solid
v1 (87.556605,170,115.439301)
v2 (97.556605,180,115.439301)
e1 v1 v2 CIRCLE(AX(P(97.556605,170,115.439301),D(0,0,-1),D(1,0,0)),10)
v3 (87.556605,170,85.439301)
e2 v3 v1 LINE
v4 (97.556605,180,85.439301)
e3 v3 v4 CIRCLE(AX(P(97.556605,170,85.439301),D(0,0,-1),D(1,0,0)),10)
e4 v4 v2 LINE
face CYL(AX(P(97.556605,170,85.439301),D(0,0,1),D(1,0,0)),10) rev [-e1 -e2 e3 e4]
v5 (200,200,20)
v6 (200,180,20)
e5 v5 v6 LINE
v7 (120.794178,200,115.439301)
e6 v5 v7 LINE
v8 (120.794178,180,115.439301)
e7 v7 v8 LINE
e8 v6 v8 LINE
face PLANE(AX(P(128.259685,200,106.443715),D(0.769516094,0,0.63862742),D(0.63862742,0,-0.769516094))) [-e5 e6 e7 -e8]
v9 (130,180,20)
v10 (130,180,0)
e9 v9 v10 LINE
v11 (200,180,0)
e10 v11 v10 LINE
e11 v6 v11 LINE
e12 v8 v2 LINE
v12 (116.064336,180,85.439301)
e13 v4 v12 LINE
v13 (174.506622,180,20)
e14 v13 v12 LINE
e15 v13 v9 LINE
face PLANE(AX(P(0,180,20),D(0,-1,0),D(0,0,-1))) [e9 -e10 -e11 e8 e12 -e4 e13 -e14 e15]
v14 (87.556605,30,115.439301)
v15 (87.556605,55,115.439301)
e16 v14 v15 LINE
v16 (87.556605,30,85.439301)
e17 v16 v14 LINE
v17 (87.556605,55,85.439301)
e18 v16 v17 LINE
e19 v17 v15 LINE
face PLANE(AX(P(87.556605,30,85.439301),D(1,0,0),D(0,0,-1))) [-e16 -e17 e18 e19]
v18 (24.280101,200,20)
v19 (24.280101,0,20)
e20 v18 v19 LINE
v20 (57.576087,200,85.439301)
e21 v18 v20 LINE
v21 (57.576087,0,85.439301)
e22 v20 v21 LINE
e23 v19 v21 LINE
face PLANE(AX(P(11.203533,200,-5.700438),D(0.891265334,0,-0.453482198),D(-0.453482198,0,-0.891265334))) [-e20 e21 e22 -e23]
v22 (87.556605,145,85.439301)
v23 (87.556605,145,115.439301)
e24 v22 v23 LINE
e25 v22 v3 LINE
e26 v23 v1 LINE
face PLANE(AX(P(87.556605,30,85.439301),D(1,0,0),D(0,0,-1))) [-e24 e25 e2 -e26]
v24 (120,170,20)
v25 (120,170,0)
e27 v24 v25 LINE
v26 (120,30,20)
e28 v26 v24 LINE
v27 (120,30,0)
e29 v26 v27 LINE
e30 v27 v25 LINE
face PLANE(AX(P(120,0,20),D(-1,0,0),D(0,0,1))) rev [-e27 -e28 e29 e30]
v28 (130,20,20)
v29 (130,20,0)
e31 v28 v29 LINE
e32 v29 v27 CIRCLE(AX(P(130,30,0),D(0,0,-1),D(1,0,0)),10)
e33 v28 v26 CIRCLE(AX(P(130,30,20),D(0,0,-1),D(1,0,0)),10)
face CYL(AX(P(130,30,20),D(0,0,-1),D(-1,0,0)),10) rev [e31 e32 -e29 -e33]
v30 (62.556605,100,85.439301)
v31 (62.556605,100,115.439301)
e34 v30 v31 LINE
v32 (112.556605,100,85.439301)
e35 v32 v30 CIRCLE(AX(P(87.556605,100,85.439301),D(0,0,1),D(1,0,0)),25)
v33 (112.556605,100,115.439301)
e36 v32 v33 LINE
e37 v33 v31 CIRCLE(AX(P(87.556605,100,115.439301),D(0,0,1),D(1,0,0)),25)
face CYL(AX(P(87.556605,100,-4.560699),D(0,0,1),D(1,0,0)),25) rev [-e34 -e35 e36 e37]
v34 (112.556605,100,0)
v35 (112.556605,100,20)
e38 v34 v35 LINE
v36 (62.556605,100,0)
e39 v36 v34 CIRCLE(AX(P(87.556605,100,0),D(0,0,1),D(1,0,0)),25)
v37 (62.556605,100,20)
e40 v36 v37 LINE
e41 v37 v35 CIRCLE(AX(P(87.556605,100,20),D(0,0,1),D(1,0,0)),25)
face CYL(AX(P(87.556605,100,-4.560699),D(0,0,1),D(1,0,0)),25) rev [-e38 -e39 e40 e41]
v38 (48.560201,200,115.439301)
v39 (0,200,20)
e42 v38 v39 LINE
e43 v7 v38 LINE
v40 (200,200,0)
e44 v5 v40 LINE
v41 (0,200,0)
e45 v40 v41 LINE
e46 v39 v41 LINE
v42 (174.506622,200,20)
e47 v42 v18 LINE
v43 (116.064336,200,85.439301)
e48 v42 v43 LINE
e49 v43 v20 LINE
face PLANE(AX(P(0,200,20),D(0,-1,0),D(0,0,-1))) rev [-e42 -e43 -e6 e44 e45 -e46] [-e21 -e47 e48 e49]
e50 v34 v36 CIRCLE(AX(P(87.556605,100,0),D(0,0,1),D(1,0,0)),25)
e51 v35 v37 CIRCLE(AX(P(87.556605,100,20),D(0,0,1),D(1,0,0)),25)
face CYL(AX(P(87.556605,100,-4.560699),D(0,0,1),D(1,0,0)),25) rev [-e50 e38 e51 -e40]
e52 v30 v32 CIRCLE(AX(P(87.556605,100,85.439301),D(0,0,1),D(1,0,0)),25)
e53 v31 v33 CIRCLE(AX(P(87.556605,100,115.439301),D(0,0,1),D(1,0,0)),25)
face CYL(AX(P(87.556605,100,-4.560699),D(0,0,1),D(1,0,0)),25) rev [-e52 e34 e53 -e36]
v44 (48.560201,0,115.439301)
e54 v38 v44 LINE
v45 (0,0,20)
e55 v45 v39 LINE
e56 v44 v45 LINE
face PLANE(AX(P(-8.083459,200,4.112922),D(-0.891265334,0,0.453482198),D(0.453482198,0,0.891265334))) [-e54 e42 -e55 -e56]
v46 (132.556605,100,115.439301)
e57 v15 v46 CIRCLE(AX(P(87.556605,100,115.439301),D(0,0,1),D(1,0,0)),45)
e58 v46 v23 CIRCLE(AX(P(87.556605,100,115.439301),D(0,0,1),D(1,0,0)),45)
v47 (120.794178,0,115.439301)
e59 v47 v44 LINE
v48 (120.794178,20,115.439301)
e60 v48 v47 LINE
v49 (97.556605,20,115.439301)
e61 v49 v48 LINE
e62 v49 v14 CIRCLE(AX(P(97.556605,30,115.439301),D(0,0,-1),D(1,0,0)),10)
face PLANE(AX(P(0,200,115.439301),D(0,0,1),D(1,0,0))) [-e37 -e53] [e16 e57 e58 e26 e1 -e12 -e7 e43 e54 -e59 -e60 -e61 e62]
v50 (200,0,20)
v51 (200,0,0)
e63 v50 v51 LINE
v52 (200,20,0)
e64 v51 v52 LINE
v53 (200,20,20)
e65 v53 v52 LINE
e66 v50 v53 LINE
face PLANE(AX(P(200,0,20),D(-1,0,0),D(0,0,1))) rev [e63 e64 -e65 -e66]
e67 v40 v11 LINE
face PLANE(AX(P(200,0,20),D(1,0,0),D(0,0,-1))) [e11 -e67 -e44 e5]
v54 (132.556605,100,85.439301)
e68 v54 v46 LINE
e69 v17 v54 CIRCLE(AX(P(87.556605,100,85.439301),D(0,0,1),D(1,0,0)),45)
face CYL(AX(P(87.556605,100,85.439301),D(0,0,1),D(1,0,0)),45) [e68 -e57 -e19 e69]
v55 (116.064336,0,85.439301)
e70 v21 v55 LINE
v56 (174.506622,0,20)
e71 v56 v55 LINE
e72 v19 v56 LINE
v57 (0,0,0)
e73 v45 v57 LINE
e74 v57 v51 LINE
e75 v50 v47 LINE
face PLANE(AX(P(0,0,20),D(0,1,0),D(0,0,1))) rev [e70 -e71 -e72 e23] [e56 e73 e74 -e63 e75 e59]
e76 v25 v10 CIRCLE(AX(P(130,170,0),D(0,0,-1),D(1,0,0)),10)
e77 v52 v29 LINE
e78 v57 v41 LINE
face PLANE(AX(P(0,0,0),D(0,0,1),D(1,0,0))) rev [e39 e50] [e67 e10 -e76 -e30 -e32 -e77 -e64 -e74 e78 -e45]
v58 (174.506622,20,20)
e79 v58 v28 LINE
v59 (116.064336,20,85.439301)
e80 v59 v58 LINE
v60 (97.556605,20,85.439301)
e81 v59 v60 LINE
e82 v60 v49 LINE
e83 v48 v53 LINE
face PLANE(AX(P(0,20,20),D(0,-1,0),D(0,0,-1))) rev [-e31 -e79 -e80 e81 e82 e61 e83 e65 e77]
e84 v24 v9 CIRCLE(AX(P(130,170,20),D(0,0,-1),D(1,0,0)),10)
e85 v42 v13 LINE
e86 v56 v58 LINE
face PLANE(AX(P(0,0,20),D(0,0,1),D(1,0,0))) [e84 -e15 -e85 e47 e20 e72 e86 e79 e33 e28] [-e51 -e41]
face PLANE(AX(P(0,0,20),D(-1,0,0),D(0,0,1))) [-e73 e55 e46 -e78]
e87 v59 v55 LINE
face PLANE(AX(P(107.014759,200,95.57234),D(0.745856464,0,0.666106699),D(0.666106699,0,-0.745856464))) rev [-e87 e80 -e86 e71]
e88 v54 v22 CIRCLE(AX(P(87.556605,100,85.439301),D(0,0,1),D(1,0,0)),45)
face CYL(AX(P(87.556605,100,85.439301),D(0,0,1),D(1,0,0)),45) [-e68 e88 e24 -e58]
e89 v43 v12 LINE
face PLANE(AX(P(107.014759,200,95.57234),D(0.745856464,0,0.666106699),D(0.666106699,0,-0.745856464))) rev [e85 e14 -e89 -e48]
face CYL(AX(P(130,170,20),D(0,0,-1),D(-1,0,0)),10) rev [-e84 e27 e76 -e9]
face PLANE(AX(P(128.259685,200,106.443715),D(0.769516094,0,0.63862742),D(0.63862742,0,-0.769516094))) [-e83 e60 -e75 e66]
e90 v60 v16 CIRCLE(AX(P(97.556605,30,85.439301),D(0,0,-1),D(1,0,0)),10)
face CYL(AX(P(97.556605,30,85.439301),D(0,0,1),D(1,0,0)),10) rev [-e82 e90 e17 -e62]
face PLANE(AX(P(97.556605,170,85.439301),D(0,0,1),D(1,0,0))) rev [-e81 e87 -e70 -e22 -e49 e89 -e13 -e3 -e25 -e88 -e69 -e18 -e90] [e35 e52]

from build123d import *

# Parameters (mm, degrees)
BASE_PROFILE_20MM_DEPTH   = 20
A_FRAME_BODY_200MM_DEPTH  = 200
FRAME_WINDOW_1_SKETCH_W   = 124.025088206
FRAME_WINDOW_1_SKETCH_H   = 160
FRAME_WINDOW_1_CUT_DEPTH  = 30
FRAME_WINDOW_2_SKETCH_W   = 43.365918468
FRAME_WINDOW_2_SKETCH_H   = 160
FRAME_WINDOW_2_CUT_DEPTH  = 30
THROUGH_OPENING_SKETCH_W  = 51.957421724
THROUGH_OPENING_SKETCH_H  = 25.341390787
THROUGH_OPENING_CUT_DEPTH = 200
WEB_BOSS_30MM_DEPTH       = 30
HUB_BOSS_30MM_DEPTH       = 30
HUB_BORE_SKETCH_R         = 25
HUB_BORE_CUT_DEPTH        = 120


with BuildPart() as part:
    # Base Profile Sketch → Base Profile 20mm (new body)
    with BuildSketch(Plane.XY):
        with BuildLine():
            Line((0, 200), (0, 0))
            Line((0, 0), (200, 0))
            Line((200, 0), (200, 20))
            Line((200, 20), (130, 20))
            ThreePointArc((130, 20), (122.928932188, 22.928932188), (120, 30))
            Line((120, 30), (120, 160))
            Line((120, 160), (120, 170))
            ThreePointArc((120, 170), (122.928932188, 177.071067812), (130, 180))
            Line((130, 180), (200, 180))
            Line((200, 180), (200, 200))
            Line((200, 200), (0, 200))
        make_face()
    extrude(amount=BASE_PROFILE_20MM_DEPTH)

    # Frame Profile Sketch → A-Frame Body 200mm (add)
    with BuildSketch(Plane.XZ):
        Polygon((120.794177907, 115.439301395), (94.123171193, 115.439301395), (91.530156651, 115.439301395), (48.56020139, 115.439301395), (0, 20), (24.280100695, 20), (59.946420611, 90.097910608), (111.903842335, 90.097910608), (174.506621983, 20), (200, 20), align=None)
    extrude(amount=-A_FRAME_BODY_200MM_DEPTH)

    # Frame Window 1 Sketch → Frame Window 1 Cut (cut)
    with BuildSketch(Plane(origin=(128.259685241, 0, 106.443715141), x_dir=(0.6386274199814919, 0, -0.7695160936899132), z_dir=(0.7695160936899134, 0, 0.6386274199814919))):
        with Locations((50.32261802, 100)):
            Rectangle(FRAME_WINDOW_1_SKETCH_W, FRAME_WINDOW_1_SKETCH_H)
    extrude(amount=-FRAME_WINDOW_1_CUT_DEPTH, mode=Mode.SUBTRACT)

    # Frame Window 2 Sketch → Frame Window 2 Cut (cut)
    with BuildSketch(Plane.XY.offset(115.439301395)):
        with Locations((99.111218673, 100)):
            Rectangle(FRAME_WINDOW_2_SKETCH_W, FRAME_WINDOW_2_SKETCH_H)
    extrude(amount=-FRAME_WINDOW_2_CUT_DEPTH, mode=Mode.SUBTRACT)

    # Through Opening Sketch → Through Opening Cut (cut)
    with BuildSketch(Plane.XZ):
        with Locations((85.925131473, 102.768606002)):
            Rectangle(THROUGH_OPENING_SKETCH_W, THROUGH_OPENING_SKETCH_H)
    extrude(amount=-THROUGH_OPENING_CUT_DEPTH, mode=Mode.SUBTRACT)

    # Web Sketch → Web Boss 30mm (add)
    with BuildSketch(Plane.XY.offset(115.439301395)):
        with BuildLine():
            Line((48.56020139, 200), (120.794177907, 200))
            Line((120.794177907, 200), (120.794177907, 180))
            Line((120.794177907, 180), (97.556604563, 180))
            ThreePointArc((97.556604563, 180), (90.485536751, 177.071067812), (87.556604563, 170))
            Line((87.556604563, 170), (87.556604563, 30))
            ThreePointArc((87.556604563, 30), (90.485536751, 22.928932188), (97.556604563, 20))
            Line((97.556604563, 20), (120.794177907, 20))
            Line((120.794177907, 20), (120.794177907, 0))
            Line((120.794177907, 0), (48.56020139, 0))
            Line((48.56020139, 0), (48.56020139, 200))
        make_face()
    extrude(amount=-WEB_BOSS_30MM_DEPTH)

    # Hub Boss Sketch → Hub Boss 30mm (add)
    with BuildSketch(Plane.XY.offset(115.439301395)):
        with BuildLine():
            Line((87.556604563, 145), (87.556604563, 55))
            ThreePointArc((87.556604563, 55), (132.556604563, 100), (87.556604563, 145))
        make_face()
    extrude(amount=-HUB_BOSS_30MM_DEPTH)

    # Hub Bore Sketch → Hub Bore Cut (cut)
    with BuildSketch(Plane.XY.offset(115.439301395)):
        with Locations((87.556604563, 100)):
            Circle(HUB_BORE_SKETCH_R)
    extrude(amount=-HUB_BORE_CUT_DEPTH, mode=Mode.SUBTRACT)


solid = part.part
